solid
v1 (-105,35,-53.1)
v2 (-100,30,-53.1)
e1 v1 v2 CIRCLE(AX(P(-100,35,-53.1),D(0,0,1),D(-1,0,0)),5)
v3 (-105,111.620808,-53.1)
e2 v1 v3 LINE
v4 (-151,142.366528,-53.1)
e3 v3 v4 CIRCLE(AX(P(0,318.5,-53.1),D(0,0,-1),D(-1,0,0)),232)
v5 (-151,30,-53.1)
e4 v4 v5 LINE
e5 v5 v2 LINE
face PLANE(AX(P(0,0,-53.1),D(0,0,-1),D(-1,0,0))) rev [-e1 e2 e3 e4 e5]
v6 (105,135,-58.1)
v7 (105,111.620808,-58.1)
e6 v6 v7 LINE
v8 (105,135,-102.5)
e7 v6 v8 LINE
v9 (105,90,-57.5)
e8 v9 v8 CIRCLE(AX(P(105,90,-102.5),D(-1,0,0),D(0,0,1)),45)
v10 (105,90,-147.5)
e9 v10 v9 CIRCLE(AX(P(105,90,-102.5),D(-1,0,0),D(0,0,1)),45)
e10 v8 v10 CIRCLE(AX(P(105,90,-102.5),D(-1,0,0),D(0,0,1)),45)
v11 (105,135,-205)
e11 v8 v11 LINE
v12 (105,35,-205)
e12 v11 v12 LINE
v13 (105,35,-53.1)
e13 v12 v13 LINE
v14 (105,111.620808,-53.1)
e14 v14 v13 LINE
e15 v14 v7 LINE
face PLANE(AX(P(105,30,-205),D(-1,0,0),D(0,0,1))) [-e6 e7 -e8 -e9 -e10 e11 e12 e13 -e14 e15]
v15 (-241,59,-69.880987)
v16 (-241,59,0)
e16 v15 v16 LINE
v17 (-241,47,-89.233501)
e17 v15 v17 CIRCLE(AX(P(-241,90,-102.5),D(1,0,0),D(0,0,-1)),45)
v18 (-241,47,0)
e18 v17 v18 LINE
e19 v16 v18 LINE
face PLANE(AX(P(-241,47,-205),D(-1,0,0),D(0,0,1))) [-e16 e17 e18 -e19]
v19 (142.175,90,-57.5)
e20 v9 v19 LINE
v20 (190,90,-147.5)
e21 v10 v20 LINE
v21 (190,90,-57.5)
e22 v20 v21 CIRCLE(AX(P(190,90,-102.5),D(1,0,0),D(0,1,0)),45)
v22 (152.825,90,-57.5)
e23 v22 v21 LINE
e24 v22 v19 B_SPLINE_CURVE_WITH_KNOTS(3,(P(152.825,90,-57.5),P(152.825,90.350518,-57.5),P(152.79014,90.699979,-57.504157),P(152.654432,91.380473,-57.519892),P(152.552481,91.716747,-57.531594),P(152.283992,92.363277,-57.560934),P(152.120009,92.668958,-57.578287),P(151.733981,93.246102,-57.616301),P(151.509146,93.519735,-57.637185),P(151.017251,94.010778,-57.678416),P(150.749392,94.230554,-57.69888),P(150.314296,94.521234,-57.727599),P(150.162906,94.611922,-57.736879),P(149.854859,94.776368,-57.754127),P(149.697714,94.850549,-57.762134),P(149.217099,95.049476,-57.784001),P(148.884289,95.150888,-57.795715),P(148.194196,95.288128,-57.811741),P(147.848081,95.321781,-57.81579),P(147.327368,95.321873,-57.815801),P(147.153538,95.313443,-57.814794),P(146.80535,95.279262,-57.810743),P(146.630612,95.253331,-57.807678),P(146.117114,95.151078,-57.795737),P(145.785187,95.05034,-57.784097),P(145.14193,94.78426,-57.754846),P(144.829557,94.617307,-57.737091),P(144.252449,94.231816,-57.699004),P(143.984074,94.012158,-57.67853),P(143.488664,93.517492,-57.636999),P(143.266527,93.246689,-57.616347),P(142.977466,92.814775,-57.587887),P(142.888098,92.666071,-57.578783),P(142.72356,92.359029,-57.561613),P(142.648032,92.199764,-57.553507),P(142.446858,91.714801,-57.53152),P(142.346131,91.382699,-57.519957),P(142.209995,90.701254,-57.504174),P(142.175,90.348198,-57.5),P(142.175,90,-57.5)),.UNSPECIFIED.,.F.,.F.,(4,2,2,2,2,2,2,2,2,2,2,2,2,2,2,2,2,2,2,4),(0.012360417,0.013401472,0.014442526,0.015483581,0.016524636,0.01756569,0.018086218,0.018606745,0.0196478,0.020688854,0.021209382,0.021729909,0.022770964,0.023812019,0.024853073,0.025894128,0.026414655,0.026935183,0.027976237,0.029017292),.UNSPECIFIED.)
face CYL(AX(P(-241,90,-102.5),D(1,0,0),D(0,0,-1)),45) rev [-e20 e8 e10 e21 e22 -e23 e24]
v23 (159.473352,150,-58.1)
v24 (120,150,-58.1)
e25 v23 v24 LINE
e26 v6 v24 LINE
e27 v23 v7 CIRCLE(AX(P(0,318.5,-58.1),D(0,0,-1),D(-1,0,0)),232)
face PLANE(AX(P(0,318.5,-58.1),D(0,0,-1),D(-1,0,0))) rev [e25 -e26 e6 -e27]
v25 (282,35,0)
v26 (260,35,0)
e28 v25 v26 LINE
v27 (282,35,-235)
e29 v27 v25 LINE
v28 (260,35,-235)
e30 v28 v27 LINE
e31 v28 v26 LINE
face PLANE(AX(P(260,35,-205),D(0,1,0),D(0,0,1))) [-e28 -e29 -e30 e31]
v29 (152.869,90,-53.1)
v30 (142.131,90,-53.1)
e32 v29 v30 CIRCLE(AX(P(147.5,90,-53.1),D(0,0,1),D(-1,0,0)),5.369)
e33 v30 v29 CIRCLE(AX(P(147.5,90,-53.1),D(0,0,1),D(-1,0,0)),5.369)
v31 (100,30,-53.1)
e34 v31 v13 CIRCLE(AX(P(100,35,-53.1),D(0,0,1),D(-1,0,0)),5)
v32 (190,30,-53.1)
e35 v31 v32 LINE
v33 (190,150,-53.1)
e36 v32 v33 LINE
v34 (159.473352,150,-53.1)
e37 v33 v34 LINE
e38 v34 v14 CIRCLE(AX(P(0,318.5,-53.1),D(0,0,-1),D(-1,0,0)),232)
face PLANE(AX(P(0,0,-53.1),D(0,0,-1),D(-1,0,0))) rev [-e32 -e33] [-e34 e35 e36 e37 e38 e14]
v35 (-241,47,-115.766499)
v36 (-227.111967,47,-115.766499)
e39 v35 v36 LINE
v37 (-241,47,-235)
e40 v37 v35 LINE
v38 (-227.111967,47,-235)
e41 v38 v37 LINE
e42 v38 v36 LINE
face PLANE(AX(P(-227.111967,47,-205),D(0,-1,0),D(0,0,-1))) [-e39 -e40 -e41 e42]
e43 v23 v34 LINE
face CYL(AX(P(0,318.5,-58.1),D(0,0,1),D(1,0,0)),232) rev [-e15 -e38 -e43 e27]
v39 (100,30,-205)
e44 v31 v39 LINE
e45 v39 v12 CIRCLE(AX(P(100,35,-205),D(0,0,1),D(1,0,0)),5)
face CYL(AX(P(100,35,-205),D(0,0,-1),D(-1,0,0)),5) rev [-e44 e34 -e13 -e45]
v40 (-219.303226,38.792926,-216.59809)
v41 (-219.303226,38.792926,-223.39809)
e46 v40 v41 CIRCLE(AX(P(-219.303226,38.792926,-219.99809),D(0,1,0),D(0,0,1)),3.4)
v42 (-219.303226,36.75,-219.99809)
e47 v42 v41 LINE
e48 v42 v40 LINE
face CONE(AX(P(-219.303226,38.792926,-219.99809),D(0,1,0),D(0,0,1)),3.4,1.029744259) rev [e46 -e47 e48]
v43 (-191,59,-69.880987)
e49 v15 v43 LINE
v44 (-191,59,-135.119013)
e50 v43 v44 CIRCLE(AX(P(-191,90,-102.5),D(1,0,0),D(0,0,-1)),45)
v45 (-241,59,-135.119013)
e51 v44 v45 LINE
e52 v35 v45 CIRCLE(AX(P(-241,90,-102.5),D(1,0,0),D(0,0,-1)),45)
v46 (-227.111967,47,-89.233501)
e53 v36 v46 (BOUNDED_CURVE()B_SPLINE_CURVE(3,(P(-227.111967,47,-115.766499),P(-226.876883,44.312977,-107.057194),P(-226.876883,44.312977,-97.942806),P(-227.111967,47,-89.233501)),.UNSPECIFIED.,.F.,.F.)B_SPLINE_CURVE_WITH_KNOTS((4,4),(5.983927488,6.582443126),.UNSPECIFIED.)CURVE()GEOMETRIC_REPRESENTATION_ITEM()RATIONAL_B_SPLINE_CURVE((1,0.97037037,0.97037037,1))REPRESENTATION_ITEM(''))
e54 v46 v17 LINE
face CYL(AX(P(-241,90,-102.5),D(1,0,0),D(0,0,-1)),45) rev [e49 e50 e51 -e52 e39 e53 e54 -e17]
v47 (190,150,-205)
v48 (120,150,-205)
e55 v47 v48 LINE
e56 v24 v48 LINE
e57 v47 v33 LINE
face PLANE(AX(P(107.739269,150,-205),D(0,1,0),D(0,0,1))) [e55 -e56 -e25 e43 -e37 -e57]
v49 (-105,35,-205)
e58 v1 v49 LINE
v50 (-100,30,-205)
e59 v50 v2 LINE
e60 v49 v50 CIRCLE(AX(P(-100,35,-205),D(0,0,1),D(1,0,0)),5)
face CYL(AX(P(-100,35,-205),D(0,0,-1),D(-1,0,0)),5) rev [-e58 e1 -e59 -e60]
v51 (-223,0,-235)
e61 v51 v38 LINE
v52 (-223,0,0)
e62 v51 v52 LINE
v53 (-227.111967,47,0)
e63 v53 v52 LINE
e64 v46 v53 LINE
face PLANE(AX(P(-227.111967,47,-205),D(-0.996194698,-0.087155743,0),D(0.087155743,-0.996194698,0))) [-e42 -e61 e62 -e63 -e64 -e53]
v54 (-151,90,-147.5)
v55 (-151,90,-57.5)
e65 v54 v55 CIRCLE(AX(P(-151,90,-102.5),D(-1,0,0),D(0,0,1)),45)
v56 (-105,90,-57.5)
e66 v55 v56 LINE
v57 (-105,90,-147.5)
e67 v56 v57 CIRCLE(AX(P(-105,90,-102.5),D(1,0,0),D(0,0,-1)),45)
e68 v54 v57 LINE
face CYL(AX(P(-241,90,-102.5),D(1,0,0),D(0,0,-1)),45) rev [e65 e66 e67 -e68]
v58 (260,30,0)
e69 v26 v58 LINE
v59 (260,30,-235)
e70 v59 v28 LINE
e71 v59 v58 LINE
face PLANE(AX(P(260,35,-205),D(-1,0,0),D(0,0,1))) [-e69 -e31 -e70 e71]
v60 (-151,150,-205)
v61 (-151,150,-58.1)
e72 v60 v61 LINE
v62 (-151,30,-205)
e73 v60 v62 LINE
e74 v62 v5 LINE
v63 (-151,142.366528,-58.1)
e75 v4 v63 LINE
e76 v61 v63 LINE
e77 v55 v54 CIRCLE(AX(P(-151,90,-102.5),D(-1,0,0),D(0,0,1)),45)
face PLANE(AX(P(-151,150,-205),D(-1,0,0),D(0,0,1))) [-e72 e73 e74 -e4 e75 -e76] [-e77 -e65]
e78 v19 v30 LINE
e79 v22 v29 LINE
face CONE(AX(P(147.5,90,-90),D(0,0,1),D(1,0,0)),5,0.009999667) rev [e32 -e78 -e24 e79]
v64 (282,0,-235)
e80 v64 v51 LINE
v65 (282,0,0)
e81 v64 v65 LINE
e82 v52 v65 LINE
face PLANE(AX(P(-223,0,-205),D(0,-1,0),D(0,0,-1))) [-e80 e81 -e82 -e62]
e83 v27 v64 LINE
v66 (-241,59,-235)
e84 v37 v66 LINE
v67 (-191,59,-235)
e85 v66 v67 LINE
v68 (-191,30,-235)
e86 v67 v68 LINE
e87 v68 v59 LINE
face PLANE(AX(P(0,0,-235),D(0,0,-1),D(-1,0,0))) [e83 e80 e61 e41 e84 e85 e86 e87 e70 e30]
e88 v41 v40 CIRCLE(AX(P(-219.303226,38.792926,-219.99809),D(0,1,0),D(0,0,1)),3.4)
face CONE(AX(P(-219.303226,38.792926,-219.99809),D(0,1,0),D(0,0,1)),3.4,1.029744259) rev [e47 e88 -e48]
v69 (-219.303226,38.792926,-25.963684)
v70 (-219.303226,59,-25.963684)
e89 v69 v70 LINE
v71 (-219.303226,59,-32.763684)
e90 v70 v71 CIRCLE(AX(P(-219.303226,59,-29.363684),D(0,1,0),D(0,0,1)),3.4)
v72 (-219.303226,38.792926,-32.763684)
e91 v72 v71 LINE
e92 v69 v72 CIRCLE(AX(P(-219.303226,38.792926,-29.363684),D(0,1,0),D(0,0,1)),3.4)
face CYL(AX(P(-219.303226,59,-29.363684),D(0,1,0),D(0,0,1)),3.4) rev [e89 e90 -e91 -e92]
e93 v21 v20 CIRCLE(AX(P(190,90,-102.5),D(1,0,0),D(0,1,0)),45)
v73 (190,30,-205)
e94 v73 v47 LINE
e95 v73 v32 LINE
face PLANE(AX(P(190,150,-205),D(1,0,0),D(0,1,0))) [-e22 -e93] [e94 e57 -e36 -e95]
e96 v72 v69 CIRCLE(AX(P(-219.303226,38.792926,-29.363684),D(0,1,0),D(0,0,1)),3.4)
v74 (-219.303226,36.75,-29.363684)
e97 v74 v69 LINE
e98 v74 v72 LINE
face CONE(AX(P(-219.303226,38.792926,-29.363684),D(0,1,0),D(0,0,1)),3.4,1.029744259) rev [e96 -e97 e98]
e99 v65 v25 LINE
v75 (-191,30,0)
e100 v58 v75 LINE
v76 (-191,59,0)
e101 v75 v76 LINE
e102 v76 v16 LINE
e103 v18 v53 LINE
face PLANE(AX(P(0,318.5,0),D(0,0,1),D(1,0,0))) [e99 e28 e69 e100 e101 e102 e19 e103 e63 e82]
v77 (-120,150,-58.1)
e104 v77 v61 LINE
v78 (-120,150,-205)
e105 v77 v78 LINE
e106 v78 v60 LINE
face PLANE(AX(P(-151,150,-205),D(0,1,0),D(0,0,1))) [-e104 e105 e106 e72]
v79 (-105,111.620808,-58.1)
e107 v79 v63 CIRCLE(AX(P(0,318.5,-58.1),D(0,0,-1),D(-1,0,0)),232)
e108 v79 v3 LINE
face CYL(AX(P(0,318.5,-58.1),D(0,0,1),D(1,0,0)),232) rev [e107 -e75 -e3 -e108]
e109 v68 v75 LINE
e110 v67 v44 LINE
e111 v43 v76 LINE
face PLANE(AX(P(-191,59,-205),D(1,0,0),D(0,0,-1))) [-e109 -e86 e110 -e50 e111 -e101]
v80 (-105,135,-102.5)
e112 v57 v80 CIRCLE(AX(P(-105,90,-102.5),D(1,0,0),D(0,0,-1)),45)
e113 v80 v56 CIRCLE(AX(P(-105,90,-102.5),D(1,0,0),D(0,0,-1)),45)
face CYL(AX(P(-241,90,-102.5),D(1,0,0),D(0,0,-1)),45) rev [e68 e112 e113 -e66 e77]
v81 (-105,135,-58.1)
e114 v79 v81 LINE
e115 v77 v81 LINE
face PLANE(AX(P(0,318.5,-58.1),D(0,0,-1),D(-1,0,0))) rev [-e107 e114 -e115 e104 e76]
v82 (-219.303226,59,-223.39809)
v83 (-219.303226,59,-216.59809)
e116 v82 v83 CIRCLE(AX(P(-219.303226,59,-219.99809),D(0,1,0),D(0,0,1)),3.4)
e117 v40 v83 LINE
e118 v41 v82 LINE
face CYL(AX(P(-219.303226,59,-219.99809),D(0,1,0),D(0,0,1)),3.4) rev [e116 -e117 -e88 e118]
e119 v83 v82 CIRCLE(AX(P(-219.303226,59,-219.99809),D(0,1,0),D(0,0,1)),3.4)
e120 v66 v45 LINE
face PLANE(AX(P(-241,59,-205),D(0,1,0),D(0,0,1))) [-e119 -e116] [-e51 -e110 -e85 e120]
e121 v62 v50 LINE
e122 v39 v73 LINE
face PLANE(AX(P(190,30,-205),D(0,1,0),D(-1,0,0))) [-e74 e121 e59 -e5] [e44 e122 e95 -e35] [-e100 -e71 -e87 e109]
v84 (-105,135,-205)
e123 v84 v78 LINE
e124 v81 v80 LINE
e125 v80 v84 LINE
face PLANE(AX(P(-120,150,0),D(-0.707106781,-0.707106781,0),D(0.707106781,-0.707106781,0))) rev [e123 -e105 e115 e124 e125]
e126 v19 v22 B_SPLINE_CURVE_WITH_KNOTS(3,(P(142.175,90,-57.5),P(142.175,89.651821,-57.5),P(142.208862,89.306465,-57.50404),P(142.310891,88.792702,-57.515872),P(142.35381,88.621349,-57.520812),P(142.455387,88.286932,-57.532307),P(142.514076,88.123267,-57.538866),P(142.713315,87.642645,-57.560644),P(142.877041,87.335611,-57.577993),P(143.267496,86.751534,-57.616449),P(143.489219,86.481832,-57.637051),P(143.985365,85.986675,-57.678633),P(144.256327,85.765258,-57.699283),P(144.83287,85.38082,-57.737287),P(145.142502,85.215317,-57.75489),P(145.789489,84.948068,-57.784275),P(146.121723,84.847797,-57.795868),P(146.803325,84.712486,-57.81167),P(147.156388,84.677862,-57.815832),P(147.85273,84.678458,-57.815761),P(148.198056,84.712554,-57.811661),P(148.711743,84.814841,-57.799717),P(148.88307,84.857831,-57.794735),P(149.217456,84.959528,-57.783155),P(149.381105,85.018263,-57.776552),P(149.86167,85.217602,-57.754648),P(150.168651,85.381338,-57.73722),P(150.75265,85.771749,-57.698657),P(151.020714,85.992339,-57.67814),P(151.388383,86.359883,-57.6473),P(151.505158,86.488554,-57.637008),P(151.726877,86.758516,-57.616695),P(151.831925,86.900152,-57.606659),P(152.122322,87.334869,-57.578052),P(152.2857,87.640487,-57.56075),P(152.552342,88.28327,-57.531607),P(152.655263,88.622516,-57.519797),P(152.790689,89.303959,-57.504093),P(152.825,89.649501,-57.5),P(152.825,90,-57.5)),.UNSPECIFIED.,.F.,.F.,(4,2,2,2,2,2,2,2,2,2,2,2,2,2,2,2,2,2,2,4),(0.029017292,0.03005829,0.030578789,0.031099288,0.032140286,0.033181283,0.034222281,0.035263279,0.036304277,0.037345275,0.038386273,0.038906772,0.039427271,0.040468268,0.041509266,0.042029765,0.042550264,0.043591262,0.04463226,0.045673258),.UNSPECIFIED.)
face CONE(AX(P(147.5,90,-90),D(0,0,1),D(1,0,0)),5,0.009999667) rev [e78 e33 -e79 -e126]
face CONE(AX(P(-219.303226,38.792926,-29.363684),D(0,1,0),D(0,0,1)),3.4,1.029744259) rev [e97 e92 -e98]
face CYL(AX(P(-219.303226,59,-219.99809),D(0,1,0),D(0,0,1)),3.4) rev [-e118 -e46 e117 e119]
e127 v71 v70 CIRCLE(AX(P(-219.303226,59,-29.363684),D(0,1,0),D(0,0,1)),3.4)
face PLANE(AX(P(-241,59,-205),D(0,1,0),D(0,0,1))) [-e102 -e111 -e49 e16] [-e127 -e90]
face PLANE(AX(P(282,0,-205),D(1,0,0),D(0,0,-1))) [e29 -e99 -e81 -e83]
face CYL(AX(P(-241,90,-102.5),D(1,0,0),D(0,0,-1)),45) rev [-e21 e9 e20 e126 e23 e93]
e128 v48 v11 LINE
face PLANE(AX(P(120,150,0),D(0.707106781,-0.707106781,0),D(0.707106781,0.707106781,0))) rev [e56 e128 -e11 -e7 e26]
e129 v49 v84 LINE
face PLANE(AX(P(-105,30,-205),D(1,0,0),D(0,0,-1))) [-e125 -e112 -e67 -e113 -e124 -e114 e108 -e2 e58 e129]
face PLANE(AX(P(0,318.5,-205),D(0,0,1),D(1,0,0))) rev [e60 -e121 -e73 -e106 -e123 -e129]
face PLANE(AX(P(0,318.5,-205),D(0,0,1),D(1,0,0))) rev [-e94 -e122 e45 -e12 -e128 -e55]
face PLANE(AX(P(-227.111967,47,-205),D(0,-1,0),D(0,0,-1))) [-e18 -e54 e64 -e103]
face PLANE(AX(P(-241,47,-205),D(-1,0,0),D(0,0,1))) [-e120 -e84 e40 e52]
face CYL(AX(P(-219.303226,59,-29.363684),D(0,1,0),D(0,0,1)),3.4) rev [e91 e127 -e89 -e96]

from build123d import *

# Parameters (mm, degrees)
BOSS_EXTRUDE1_DEPTH     = 205
FILLET1_R               = 5
SKETCH2_R               = 45
CUT_EXTRUDE1_DEPTH      = 582.424113707
CUT_EXTRUDE2_DEPTH      = 380.537876952
CUT_EXTRUDE3_DEPTH      = 5
CUT_EXTRUDE3_DEPTH_BACK = 354.691405041
SKETCH5_R               = 232
BOSS_EXTRUDE2_DEPTH     = 30
CUT_EXTRUDE4_DEPTH      = 53.1
M8_TAPPED_HOLE1_D       = 6.8
M8_TAPPED_HOLE1_DEPTH   = 20.207073895
M8_TAPPED_HOLE1_TIP     = 2.042926105


with BuildPart() as part:
    # Sketch1 → Boss-Extrude1 (new body)
    with BuildSketch(Plane.XY):
        with BuildLine():
            Line((-227.111967186, 47), (-223, 0))
            Line((-223, 0), (282, 0))
            Line((282, 0), (282, 35))
            Line((282, 35), (260, 35))
            Line((260, 35), (260, 30))
            Line((260, 30), (190, 30))
            Line((190, 30), (190, 150))
            Line((190, 150), (107.739268607, 150))
            ThreePointArc((107.739268607, 150), (106.373112603, 149.134239248), (105, 148.279554695))
            Line((105, 148.279554695), (105, 30))
            Line((105, 30), (-105, 30))
            Line((-105, 30), (-105, 148.279554695))
            ThreePointArc((-105, 148.279554695), (-106.373112603, 149.134239248), (-107.739268607, 150))
            Line((-107.739268607, 150), (-151, 150))
            Line((-151, 150), (-151, 30))
            Line((-151, 30), (-191, 30))
            Line((-191, 30), (-191, 59))
            Line((-191, 59), (-241, 59))
            Line((-241, 59), (-241, 47))
            Line((-241, 47), (-227.111967186, 47))
        make_face()
    extrude(amount=-BOSS_EXTRUDE1_DEPTH)

    # Fillet1
    fillet1_edges = [part.edges().sort_by_distance(p)[0] for p in [
        (-105, 30, -102.5),
        (105, 30, -102.5),
    ]]
    fillet(fillet1_edges, radius=FILLET1_R)

    # Sketch2 → Cut-Extrude1 (cut, through all)
    with BuildSketch(Plane(origin=(282, 0, 0), x_dir=(0, 0, -1), z_dir=(1, 0, 0))):
        with Locations((102.5, 90)):
            Circle(SKETCH2_R)
    extrude(amount=-CUT_EXTRUDE1_DEPTH, mode=Mode.SUBTRACT)

    # Sketch3 → Cut-Revolve1 (revolve, cut)
    with BuildSketch(Plane(origin=(147.5, 0, 0), x_dir=(0, 0, -1), z_dir=(1, 0, 0)), mode=Mode.PRIVATE) as cut_revolve1_sk:
        Polygon((0, 95.9), (0, 90), (90, 90), (90, 95), align=None)
    revolve(cut_revolve1_sk.sketch.rotate(Axis((147.5, 90, -102.5), (0, 0, 1)), 136.455003644), axis=Axis((147.5, 90, -102.5), (0, 0, 1)), mode=Mode.SUBTRACT)

    # Sketch4 → Cut-Extrude2 (cut, through all)
    with BuildSketch(Plane(origin=(0, 0, -205), x_dir=(-1, 0, 0), z_dir=(0, 0, -1))):
        Polygon((-120, 150), (-105, 135), (-105, 150), align=None)
        Polygon((105, 150), (120, 150), (105, 135), align=None)
    extrude(amount=-CUT_EXTRUDE2_DEPTH, mode=Mode.SUBTRACT)

    # Sketch5 → Cut-Extrude3 (cut, two sides: drawn at the far end of the back side and taken through both)
    with BuildSketch(Plane(origin=(0, 0, -53.1), x_dir=(-1, 0, 0), z_dir=(0, 0, -1)).offset(-CUT_EXTRUDE3_DEPTH_BACK)):
        with Locations((0, 318.5)):
            Circle(SKETCH5_R)
    extrude(amount=CUT_EXTRUDE3_DEPTH + CUT_EXTRUDE3_DEPTH_BACK, mode=Mode.SUBTRACT)

    # Sketch6 → Boss-Extrude2 (add)
    with BuildSketch(Plane(origin=(0, 0, -205), x_dir=(-1, 0, 0), z_dir=(0, 0, -1))):
        Polygon((-282, 0), (223, 0), (227.111967186, 47), (241, 47), (241, 59), (191, 59), (191, 30), (-260, 30), (-260, 35), (-282, 35), align=None)
    extrude(amount=BOSS_EXTRUDE2_DEPTH)

    # Sketch7 → Cut-Extrude4 (cut)
    with BuildSketch(Plane.XY):
        Polygon((-151, 30), (-151, 146.183263941), (-120, 150), (-105, 135), (-105, 35), (-100, 30), align=None)
        Polygon((190, 150), (190, 30), (100, 30), (105, 35), (105, 135), (120, 150), align=None)
    extrude(amount=-CUT_EXTRUDE4_DEPTH, mode=Mode.SUBTRACT)

    # M8 Tapped Hole1
    with Locations(Plane(origin=(0, 59, 0), x_dir=(1, 0, 0), z_dir=(0, 1, 0))):
        with Locations((271, 29.3636836), (271, 219.953225124), (-219.303225542, 219.998090208), (-219.303225542, 29.3636836)):
            Hole(M8_TAPPED_HOLE1_D / 2, depth=M8_TAPPED_HOLE1_DEPTH)
            with Locations((0, 0, -(M8_TAPPED_HOLE1_DEPTH + M8_TAPPED_HOLE1_TIP / 2))):  # 118° drill point
                Cone(0, M8_TAPPED_HOLE1_D / 2, M8_TAPPED_HOLE1_TIP, mode=Mode.SUBTRACT)


solid = part.part
